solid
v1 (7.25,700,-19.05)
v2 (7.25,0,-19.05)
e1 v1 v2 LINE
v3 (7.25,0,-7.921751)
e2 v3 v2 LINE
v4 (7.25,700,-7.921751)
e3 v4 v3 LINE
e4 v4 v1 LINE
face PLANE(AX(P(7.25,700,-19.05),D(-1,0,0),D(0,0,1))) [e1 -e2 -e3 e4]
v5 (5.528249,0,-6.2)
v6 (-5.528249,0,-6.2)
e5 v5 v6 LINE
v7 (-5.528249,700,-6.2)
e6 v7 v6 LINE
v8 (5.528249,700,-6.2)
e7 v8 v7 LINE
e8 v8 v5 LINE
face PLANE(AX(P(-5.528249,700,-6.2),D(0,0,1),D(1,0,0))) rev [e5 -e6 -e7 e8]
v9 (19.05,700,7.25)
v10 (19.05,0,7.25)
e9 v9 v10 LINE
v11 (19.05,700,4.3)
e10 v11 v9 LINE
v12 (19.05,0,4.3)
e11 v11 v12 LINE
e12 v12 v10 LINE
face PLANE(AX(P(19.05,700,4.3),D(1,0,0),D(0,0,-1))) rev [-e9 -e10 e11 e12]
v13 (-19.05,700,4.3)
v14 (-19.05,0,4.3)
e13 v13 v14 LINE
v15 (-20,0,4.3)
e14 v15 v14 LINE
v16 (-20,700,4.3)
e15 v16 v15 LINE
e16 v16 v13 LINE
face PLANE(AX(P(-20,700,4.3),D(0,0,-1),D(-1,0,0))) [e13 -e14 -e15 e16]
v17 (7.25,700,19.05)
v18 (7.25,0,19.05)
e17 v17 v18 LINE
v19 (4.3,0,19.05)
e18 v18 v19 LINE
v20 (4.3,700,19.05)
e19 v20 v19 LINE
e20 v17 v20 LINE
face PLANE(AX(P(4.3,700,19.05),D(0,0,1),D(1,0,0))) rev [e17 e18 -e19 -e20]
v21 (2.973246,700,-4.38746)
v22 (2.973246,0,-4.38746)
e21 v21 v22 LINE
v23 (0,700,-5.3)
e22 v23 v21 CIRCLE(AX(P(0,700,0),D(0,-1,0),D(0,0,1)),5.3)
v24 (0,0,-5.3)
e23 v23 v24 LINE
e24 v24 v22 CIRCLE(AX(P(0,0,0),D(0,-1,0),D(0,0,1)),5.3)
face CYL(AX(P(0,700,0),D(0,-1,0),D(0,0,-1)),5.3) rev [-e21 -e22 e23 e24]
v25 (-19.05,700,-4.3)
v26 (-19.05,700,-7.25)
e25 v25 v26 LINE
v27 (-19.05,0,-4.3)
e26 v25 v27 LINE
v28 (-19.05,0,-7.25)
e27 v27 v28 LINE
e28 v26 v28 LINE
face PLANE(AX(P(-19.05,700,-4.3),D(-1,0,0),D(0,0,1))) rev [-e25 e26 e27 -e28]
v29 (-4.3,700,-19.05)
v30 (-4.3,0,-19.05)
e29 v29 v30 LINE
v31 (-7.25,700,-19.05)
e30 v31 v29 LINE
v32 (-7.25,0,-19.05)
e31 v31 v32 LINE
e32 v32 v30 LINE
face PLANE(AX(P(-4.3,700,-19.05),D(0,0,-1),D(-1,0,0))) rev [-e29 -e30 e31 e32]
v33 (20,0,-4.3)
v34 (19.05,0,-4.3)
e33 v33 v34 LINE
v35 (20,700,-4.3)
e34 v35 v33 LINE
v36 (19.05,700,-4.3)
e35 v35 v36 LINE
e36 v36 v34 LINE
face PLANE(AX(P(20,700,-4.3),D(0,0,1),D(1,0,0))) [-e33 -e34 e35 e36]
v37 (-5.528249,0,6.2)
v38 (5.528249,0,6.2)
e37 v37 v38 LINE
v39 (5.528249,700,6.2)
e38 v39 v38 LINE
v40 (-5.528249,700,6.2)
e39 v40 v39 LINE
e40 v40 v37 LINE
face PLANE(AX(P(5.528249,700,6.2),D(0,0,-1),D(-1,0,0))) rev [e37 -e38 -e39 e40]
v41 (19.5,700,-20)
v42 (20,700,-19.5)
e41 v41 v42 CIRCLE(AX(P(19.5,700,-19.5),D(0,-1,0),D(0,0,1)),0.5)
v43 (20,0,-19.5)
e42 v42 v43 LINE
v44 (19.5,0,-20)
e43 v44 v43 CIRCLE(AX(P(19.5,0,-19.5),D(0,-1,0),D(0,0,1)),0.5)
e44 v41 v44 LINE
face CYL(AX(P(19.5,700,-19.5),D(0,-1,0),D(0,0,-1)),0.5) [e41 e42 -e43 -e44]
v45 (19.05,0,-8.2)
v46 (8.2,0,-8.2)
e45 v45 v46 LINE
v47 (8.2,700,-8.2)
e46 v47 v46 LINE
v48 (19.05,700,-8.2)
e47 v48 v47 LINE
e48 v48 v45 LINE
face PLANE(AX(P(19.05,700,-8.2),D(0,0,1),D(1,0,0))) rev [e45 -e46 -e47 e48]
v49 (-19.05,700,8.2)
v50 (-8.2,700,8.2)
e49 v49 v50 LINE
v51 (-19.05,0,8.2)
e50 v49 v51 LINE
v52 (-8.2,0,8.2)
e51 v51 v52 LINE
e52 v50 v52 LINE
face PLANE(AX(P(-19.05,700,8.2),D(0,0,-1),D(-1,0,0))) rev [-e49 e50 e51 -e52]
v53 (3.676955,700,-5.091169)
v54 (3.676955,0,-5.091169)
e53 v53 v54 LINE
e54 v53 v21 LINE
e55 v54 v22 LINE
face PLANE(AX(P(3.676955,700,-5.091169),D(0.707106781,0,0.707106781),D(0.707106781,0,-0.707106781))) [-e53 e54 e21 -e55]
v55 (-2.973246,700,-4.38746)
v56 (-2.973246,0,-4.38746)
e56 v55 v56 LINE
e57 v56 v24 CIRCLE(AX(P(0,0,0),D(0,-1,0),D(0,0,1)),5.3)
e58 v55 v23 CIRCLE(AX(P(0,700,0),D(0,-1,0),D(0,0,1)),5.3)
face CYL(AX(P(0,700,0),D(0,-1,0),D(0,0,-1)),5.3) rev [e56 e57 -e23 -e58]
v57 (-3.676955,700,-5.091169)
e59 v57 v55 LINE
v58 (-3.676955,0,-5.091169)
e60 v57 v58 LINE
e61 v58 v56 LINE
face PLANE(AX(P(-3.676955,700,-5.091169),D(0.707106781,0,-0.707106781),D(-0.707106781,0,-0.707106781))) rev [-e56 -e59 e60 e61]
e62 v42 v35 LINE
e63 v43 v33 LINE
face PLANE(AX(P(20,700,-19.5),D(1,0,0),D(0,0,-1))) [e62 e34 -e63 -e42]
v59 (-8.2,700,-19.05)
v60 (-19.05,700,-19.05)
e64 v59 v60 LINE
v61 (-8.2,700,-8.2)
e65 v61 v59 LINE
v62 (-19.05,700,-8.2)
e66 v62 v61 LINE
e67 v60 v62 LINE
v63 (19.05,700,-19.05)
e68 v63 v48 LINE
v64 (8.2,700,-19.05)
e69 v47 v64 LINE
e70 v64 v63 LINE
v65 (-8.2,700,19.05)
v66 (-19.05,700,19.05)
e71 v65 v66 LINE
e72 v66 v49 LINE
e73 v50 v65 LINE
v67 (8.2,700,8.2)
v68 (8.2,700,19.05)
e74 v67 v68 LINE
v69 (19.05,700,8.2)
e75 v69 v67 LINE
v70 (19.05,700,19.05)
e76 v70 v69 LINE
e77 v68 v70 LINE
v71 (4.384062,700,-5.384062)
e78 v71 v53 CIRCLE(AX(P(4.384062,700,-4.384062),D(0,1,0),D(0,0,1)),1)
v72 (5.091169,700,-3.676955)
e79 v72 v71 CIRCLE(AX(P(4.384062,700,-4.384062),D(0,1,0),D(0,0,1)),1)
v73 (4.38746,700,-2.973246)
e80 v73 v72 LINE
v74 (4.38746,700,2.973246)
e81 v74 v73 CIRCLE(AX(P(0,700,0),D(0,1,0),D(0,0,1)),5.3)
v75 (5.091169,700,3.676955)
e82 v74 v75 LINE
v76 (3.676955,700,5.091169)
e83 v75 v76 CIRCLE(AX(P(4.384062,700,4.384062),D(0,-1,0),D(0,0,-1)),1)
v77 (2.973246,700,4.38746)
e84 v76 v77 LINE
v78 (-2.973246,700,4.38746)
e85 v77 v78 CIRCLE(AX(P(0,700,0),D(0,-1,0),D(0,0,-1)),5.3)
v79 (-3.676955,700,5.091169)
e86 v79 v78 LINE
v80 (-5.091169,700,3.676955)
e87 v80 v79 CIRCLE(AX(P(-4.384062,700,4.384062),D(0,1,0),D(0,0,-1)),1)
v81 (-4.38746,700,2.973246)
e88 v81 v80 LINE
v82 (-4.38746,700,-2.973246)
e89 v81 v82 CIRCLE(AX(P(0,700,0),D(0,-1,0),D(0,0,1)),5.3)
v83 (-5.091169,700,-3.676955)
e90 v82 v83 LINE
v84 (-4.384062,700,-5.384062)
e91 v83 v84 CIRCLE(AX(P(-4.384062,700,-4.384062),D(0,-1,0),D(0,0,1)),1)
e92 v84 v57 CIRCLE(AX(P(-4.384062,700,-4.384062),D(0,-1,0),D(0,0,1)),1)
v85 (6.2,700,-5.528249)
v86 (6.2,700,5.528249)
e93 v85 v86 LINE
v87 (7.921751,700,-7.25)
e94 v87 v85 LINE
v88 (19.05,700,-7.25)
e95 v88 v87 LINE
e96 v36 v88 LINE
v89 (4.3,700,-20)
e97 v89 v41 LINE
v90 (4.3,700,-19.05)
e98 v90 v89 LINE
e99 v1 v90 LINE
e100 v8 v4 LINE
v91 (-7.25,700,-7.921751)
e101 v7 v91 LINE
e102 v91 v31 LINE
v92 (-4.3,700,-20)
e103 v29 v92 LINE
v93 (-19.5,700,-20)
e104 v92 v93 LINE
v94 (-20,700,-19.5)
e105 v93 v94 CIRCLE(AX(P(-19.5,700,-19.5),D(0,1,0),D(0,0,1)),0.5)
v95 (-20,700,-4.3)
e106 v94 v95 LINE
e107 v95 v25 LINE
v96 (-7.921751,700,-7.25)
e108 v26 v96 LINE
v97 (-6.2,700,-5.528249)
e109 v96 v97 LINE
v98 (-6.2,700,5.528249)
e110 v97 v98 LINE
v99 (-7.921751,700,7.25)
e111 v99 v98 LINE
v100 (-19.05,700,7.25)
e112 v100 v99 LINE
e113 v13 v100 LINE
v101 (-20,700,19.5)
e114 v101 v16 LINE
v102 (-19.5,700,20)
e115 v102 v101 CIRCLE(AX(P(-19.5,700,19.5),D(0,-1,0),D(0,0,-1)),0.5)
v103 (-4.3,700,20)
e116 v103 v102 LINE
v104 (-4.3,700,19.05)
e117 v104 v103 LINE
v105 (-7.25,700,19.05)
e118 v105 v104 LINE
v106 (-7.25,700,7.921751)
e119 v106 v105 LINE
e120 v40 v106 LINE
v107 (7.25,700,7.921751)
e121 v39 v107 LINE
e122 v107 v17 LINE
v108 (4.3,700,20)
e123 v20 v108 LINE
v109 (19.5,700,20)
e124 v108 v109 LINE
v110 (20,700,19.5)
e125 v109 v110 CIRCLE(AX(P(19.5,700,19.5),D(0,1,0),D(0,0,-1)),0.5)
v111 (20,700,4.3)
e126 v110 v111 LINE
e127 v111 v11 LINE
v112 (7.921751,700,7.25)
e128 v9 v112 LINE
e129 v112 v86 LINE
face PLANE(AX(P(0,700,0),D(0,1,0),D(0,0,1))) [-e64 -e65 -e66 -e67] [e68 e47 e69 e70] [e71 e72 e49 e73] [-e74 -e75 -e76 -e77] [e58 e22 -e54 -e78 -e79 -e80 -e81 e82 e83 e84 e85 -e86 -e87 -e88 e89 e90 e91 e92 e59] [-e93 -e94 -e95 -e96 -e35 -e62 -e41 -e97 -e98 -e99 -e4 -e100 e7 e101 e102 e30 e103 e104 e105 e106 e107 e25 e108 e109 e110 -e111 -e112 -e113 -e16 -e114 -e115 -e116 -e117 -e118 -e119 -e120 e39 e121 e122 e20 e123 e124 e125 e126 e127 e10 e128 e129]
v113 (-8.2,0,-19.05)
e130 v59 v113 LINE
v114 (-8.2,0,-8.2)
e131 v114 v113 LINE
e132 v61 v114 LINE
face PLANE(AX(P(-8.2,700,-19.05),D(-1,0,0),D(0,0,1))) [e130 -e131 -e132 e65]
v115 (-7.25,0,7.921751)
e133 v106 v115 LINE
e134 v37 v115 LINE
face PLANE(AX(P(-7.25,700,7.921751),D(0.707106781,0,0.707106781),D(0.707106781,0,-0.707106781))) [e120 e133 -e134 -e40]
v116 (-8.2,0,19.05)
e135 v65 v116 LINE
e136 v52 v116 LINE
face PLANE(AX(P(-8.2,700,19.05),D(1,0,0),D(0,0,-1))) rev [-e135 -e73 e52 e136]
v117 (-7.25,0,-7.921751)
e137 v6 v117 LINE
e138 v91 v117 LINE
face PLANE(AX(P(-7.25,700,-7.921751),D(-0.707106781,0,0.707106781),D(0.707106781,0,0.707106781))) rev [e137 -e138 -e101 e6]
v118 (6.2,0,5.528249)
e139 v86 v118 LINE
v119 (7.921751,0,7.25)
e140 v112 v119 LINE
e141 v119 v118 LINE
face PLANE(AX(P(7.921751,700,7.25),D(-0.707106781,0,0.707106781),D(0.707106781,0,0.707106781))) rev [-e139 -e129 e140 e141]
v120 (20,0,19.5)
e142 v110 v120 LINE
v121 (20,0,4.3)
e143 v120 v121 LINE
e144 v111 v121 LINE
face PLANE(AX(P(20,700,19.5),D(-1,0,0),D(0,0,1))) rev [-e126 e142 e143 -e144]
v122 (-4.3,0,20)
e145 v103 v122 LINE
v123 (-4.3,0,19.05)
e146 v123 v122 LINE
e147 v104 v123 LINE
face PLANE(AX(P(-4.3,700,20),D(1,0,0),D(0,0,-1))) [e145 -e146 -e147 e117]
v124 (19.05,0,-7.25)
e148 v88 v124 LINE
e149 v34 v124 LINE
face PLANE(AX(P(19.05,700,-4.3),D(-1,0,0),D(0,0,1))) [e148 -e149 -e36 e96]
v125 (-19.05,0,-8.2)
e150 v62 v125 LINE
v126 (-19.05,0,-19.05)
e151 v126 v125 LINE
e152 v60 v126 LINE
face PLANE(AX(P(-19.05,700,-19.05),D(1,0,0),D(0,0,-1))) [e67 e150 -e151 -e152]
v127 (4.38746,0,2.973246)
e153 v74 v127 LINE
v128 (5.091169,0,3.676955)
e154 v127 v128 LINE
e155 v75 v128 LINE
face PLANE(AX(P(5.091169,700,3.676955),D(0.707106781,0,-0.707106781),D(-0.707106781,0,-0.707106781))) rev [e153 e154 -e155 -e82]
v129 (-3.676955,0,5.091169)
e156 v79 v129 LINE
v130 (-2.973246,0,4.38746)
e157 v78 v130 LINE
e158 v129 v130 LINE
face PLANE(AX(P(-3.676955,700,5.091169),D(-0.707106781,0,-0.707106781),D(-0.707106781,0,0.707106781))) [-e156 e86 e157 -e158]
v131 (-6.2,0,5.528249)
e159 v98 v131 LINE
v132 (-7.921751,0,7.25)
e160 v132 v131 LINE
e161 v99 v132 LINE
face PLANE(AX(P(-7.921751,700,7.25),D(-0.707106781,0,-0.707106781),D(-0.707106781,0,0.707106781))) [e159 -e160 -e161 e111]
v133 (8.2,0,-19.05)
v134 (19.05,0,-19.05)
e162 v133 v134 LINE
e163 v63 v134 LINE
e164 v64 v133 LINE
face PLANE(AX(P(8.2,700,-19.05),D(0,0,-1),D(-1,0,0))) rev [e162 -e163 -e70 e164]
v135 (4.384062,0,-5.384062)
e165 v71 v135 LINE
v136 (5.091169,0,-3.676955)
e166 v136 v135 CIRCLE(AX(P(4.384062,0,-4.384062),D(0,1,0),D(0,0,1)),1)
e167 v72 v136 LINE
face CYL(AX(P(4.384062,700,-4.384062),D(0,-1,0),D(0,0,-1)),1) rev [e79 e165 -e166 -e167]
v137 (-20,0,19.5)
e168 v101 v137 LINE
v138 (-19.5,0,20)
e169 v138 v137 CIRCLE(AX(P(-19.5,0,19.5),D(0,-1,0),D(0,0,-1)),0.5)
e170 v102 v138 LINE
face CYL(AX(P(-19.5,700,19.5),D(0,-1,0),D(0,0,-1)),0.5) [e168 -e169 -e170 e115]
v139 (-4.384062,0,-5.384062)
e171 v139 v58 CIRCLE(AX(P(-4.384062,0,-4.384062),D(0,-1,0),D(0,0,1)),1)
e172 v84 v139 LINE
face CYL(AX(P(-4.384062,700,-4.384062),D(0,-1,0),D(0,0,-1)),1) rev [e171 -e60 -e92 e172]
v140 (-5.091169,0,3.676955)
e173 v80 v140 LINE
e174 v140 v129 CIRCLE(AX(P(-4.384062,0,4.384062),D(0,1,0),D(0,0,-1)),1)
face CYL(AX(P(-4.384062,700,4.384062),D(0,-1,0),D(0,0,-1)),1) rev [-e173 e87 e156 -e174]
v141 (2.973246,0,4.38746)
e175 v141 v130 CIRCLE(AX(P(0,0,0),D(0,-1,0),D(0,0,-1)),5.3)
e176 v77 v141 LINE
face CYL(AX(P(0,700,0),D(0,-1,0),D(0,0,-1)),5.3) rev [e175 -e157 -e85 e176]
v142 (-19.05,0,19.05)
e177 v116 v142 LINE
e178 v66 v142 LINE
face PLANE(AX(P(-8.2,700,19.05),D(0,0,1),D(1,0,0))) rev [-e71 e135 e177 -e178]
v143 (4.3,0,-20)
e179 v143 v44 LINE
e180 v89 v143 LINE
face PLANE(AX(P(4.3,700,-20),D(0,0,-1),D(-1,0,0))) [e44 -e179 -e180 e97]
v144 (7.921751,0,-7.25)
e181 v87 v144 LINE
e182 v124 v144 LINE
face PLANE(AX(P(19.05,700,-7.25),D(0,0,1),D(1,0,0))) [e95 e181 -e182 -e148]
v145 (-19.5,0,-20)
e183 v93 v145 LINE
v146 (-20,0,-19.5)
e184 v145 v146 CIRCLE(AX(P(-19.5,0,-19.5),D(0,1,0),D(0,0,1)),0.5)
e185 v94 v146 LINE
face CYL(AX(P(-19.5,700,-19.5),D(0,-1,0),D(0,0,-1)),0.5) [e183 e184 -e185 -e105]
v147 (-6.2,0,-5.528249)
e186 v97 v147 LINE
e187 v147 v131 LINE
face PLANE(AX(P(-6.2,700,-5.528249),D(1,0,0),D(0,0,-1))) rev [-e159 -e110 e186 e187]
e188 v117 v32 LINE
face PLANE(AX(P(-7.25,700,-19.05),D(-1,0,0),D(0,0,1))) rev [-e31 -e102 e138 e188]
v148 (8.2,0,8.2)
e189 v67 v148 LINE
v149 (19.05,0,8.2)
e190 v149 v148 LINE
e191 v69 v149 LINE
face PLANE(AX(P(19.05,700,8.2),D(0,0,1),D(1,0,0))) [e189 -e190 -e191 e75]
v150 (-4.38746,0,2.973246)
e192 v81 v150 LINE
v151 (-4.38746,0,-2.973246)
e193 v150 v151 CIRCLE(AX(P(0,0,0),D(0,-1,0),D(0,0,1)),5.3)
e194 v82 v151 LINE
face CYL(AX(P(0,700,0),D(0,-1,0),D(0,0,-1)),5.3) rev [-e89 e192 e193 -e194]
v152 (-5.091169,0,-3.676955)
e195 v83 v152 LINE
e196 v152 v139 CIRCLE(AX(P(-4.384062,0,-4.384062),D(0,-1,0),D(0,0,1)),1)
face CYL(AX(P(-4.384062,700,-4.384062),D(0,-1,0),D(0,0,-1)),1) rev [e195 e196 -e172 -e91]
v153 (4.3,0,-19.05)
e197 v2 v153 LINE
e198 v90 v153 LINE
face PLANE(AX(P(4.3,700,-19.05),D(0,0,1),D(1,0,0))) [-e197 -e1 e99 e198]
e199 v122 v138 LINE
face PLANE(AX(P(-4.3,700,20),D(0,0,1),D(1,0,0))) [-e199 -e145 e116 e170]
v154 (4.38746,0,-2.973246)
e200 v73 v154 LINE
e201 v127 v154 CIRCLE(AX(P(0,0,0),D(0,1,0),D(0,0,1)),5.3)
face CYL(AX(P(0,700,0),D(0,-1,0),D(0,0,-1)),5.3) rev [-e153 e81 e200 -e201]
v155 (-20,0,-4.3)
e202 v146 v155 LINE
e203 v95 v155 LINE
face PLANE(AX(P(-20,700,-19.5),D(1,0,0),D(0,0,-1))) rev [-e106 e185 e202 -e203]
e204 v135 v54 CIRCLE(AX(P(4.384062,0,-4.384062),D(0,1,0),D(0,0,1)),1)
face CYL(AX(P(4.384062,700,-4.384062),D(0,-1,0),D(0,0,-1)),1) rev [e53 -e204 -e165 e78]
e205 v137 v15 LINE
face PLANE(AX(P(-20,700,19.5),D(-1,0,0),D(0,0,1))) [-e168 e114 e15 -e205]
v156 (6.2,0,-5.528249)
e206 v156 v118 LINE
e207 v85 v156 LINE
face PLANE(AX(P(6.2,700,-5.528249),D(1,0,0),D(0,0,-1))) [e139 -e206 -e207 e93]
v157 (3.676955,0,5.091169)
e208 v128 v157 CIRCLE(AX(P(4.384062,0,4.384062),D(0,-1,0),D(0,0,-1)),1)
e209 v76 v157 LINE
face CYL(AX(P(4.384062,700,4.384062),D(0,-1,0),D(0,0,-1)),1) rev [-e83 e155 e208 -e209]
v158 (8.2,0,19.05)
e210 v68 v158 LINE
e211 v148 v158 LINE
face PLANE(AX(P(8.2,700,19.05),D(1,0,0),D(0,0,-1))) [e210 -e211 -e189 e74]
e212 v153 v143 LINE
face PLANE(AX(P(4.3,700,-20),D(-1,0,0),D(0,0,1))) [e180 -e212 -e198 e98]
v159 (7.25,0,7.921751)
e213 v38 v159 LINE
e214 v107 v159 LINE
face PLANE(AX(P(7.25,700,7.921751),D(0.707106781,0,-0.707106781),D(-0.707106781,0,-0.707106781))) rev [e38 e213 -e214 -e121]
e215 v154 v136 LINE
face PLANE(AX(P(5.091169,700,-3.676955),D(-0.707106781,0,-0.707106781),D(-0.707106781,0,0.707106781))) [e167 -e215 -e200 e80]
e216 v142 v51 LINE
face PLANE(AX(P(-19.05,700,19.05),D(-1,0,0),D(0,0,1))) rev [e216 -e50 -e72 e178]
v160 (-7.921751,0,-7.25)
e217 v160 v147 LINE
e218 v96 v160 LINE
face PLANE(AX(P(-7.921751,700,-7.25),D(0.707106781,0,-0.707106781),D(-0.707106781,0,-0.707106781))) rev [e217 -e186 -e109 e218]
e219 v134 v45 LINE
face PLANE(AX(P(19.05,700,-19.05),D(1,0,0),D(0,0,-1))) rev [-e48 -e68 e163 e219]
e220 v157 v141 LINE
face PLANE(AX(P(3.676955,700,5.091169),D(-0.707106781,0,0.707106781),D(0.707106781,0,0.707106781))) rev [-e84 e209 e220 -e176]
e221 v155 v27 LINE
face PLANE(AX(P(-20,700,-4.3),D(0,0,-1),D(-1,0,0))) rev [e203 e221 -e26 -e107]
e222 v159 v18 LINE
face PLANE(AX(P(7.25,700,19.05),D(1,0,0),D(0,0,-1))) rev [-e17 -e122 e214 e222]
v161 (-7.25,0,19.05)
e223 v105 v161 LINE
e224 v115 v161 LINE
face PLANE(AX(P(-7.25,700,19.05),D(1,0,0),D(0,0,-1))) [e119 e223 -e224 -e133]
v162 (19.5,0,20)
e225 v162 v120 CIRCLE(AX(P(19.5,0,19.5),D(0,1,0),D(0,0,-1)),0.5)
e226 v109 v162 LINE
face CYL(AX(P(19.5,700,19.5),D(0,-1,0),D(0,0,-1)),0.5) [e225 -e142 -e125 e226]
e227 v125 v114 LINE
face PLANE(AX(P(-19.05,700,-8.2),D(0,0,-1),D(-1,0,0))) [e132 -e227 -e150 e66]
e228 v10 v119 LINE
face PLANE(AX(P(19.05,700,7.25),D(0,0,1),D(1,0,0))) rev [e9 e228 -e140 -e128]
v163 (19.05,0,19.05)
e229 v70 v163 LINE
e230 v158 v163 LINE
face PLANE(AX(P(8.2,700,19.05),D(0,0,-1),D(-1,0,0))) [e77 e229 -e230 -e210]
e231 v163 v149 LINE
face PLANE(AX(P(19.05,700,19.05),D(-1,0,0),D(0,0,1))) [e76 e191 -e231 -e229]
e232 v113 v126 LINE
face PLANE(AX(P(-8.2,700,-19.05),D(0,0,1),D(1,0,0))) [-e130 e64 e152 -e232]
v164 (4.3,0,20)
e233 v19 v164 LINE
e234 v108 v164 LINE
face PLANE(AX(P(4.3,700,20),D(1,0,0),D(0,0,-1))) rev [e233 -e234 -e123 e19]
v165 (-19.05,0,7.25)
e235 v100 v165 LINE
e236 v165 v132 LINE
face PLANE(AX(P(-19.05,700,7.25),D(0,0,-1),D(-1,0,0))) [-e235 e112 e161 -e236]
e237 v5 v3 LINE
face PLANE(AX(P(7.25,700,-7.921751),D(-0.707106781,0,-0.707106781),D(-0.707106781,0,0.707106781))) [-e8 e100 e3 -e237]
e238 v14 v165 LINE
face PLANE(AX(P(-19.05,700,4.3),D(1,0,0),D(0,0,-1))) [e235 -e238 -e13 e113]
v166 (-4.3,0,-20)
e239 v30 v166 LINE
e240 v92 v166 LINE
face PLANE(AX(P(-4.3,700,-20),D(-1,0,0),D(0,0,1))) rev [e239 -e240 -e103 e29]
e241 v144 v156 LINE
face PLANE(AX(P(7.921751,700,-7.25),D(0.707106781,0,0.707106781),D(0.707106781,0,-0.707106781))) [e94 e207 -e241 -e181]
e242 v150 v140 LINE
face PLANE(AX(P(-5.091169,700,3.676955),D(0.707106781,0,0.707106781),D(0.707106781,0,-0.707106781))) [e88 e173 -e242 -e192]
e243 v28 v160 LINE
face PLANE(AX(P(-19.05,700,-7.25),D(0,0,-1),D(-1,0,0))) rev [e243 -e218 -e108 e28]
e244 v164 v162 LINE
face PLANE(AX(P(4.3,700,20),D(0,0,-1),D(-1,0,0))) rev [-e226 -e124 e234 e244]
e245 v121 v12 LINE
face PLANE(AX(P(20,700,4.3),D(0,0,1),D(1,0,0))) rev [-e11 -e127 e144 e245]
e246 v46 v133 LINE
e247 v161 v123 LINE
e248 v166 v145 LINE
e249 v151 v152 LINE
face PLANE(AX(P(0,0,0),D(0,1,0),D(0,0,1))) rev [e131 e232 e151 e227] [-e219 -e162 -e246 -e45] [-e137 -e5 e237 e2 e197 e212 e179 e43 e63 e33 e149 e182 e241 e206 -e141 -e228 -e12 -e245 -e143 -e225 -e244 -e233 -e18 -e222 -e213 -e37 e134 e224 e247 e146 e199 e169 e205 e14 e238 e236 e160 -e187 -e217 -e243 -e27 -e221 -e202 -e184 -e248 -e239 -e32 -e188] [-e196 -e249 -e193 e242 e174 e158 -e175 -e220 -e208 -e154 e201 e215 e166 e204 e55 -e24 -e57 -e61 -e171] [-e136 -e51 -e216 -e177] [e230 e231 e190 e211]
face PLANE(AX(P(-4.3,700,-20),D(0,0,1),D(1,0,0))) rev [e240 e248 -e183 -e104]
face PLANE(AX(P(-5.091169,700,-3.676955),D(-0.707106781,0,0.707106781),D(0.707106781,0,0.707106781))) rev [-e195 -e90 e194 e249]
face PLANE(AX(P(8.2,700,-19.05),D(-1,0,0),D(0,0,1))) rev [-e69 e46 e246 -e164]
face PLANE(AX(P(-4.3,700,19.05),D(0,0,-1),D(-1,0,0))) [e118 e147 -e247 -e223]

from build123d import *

# Parameters (mm, degrees)
SKETCH1_W               = 10.85
SKETCH1_H               = 10.85
BOSS_EXTRUDE1_DEPTH     = 700
MIRROR2_COPY_1_SKETCH_W = 10.85
MIRROR2_COPY_1_SKETCH_H = 10.85
MIRROR2_COPY_1_DEPTH    = 700


with BuildPart() as part:
    # Sketch1 → Boss-Extrude1 (new body)
    with BuildSketch(Plane(origin=(0, 0, 0), x_dir=(1, 0, 0), z_dir=(0, 1, 0))):
        with BuildLine():
            Line((-4.3, 20), (-19.5, 20))
            ThreePointArc((-19.5, 20), (-19.853553391, 19.853553391), (-20, 19.5))
            Line((-20, 19.5), (-20, 4.3))
            Line((-20, 4.3), (-19.05, 4.3))
            Line((-19.05, 4.3), (-19.05, 7.25))
            Line((-19.05, 7.25), (-7.921751442, 7.25))
            Line((-7.921751442, 7.25), (-6.2, 5.528248558))
            Line((-6.2, 5.528248558), (-6.2, 0))
            Line((-6.2, 0), (-5.3, 0))
            ThreePointArc((-5.3, 0), (-5.066731596, 1.555066215), (-4.387460025, 2.973246463))
            Line((-4.387460025, 2.973246463), (-5.091168825, 3.676955262))
            ThreePointArc((-5.091168825, 3.676955262), (-5.091168825, 5.091168825), (-3.676955262, 5.091168825))
            Line((-3.676955262, 5.091168825), (-2.973246463, 4.387460025))
            ThreePointArc((-2.973246463, 4.387460025), (-1.555066215, 5.066731596), (0, 5.3))
            Line((0, 5.3), (0, 6.2))
            Line((0, 6.2), (-5.528248558, 6.2))
            Line((-5.528248558, 6.2), (-7.25, 7.921751442))
            Line((-7.25, 7.921751442), (-7.25, 19.05))
            Line((-7.25, 19.05), (-4.3, 19.05))
            Line((-4.3, 19.05), (-4.3, 20))
        make_face()
        with Locations((-13.625, 13.625)):
            Rectangle(SKETCH1_W, SKETCH1_H, mode=Mode.SUBTRACT)
    boss_extrude1 = extrude(amount=BOSS_EXTRUDE1_DEPTH)

    # Mirror1: Boss-Extrude1 across plane
    add(boss_extrude1.mirror(Plane(origin=(0, 0, 0), x_dir=(0, 0, 1), z_dir=(1, 0, 0))))

    # Mirror2: Boss-Extrude1 across plane
    add(boss_extrude1.mirror(Plane.XY))

    # Mirror2 copy 1 sketch → Mirror2 copy 1 (add)
    with BuildSketch(Plane(origin=(0, 0, 0), x_dir=(-1, 0, 0), z_dir=(0, 1, 0))):
        with BuildLine():
            Line((-4.3, 20), (-19.5, 20))
            ThreePointArc((-19.5, 20), (-19.853553391, 19.853553391), (-20, 19.5))
            Line((-20, 19.5), (-20, 4.3))
            Line((-20, 4.3), (-19.05, 4.3))
            Line((-19.05, 4.3), (-19.05, 7.25))
            Line((-19.05, 7.25), (-7.921751442, 7.25))
            Line((-7.921751442, 7.25), (-6.2, 5.528248558))
            Line((-6.2, 5.528248558), (-6.2, 0))
            Line((-6.2, 0), (-5.3, 0))
            ThreePointArc((-5.3, 0), (-5.066731596, 1.555066215), (-4.387460025, 2.973246463))
            Line((-4.387460025, 2.973246463), (-5.091168825, 3.676955262))
            ThreePointArc((-5.091168825, 3.676955262), (-5.091168825, 5.091168825), (-3.676955262, 5.091168825))
            Line((-3.676955262, 5.091168825), (-2.973246463, 4.387460025))
            ThreePointArc((-2.973246463, 4.387460025), (-1.555066215, 5.066731596), (0, 5.3))
            Line((0, 5.3), (0, 6.2))
            Line((0, 6.2), (-5.528248558, 6.2))
            Line((-5.528248558, 6.2), (-7.25, 7.921751442))
            Line((-7.25, 7.921751442), (-7.25, 19.05))
            Line((-7.25, 19.05), (-4.3, 19.05))
            Line((-4.3, 19.05), (-4.3, 20))
        make_face()
        with Locations((-13.625, 13.625)):
            Rectangle(MIRROR2_COPY_1_SKETCH_W, MIRROR2_COPY_1_SKETCH_H, mode=Mode.SUBTRACT)
    extrude(amount=MIRROR2_COPY_1_DEPTH)


solid = part.part
